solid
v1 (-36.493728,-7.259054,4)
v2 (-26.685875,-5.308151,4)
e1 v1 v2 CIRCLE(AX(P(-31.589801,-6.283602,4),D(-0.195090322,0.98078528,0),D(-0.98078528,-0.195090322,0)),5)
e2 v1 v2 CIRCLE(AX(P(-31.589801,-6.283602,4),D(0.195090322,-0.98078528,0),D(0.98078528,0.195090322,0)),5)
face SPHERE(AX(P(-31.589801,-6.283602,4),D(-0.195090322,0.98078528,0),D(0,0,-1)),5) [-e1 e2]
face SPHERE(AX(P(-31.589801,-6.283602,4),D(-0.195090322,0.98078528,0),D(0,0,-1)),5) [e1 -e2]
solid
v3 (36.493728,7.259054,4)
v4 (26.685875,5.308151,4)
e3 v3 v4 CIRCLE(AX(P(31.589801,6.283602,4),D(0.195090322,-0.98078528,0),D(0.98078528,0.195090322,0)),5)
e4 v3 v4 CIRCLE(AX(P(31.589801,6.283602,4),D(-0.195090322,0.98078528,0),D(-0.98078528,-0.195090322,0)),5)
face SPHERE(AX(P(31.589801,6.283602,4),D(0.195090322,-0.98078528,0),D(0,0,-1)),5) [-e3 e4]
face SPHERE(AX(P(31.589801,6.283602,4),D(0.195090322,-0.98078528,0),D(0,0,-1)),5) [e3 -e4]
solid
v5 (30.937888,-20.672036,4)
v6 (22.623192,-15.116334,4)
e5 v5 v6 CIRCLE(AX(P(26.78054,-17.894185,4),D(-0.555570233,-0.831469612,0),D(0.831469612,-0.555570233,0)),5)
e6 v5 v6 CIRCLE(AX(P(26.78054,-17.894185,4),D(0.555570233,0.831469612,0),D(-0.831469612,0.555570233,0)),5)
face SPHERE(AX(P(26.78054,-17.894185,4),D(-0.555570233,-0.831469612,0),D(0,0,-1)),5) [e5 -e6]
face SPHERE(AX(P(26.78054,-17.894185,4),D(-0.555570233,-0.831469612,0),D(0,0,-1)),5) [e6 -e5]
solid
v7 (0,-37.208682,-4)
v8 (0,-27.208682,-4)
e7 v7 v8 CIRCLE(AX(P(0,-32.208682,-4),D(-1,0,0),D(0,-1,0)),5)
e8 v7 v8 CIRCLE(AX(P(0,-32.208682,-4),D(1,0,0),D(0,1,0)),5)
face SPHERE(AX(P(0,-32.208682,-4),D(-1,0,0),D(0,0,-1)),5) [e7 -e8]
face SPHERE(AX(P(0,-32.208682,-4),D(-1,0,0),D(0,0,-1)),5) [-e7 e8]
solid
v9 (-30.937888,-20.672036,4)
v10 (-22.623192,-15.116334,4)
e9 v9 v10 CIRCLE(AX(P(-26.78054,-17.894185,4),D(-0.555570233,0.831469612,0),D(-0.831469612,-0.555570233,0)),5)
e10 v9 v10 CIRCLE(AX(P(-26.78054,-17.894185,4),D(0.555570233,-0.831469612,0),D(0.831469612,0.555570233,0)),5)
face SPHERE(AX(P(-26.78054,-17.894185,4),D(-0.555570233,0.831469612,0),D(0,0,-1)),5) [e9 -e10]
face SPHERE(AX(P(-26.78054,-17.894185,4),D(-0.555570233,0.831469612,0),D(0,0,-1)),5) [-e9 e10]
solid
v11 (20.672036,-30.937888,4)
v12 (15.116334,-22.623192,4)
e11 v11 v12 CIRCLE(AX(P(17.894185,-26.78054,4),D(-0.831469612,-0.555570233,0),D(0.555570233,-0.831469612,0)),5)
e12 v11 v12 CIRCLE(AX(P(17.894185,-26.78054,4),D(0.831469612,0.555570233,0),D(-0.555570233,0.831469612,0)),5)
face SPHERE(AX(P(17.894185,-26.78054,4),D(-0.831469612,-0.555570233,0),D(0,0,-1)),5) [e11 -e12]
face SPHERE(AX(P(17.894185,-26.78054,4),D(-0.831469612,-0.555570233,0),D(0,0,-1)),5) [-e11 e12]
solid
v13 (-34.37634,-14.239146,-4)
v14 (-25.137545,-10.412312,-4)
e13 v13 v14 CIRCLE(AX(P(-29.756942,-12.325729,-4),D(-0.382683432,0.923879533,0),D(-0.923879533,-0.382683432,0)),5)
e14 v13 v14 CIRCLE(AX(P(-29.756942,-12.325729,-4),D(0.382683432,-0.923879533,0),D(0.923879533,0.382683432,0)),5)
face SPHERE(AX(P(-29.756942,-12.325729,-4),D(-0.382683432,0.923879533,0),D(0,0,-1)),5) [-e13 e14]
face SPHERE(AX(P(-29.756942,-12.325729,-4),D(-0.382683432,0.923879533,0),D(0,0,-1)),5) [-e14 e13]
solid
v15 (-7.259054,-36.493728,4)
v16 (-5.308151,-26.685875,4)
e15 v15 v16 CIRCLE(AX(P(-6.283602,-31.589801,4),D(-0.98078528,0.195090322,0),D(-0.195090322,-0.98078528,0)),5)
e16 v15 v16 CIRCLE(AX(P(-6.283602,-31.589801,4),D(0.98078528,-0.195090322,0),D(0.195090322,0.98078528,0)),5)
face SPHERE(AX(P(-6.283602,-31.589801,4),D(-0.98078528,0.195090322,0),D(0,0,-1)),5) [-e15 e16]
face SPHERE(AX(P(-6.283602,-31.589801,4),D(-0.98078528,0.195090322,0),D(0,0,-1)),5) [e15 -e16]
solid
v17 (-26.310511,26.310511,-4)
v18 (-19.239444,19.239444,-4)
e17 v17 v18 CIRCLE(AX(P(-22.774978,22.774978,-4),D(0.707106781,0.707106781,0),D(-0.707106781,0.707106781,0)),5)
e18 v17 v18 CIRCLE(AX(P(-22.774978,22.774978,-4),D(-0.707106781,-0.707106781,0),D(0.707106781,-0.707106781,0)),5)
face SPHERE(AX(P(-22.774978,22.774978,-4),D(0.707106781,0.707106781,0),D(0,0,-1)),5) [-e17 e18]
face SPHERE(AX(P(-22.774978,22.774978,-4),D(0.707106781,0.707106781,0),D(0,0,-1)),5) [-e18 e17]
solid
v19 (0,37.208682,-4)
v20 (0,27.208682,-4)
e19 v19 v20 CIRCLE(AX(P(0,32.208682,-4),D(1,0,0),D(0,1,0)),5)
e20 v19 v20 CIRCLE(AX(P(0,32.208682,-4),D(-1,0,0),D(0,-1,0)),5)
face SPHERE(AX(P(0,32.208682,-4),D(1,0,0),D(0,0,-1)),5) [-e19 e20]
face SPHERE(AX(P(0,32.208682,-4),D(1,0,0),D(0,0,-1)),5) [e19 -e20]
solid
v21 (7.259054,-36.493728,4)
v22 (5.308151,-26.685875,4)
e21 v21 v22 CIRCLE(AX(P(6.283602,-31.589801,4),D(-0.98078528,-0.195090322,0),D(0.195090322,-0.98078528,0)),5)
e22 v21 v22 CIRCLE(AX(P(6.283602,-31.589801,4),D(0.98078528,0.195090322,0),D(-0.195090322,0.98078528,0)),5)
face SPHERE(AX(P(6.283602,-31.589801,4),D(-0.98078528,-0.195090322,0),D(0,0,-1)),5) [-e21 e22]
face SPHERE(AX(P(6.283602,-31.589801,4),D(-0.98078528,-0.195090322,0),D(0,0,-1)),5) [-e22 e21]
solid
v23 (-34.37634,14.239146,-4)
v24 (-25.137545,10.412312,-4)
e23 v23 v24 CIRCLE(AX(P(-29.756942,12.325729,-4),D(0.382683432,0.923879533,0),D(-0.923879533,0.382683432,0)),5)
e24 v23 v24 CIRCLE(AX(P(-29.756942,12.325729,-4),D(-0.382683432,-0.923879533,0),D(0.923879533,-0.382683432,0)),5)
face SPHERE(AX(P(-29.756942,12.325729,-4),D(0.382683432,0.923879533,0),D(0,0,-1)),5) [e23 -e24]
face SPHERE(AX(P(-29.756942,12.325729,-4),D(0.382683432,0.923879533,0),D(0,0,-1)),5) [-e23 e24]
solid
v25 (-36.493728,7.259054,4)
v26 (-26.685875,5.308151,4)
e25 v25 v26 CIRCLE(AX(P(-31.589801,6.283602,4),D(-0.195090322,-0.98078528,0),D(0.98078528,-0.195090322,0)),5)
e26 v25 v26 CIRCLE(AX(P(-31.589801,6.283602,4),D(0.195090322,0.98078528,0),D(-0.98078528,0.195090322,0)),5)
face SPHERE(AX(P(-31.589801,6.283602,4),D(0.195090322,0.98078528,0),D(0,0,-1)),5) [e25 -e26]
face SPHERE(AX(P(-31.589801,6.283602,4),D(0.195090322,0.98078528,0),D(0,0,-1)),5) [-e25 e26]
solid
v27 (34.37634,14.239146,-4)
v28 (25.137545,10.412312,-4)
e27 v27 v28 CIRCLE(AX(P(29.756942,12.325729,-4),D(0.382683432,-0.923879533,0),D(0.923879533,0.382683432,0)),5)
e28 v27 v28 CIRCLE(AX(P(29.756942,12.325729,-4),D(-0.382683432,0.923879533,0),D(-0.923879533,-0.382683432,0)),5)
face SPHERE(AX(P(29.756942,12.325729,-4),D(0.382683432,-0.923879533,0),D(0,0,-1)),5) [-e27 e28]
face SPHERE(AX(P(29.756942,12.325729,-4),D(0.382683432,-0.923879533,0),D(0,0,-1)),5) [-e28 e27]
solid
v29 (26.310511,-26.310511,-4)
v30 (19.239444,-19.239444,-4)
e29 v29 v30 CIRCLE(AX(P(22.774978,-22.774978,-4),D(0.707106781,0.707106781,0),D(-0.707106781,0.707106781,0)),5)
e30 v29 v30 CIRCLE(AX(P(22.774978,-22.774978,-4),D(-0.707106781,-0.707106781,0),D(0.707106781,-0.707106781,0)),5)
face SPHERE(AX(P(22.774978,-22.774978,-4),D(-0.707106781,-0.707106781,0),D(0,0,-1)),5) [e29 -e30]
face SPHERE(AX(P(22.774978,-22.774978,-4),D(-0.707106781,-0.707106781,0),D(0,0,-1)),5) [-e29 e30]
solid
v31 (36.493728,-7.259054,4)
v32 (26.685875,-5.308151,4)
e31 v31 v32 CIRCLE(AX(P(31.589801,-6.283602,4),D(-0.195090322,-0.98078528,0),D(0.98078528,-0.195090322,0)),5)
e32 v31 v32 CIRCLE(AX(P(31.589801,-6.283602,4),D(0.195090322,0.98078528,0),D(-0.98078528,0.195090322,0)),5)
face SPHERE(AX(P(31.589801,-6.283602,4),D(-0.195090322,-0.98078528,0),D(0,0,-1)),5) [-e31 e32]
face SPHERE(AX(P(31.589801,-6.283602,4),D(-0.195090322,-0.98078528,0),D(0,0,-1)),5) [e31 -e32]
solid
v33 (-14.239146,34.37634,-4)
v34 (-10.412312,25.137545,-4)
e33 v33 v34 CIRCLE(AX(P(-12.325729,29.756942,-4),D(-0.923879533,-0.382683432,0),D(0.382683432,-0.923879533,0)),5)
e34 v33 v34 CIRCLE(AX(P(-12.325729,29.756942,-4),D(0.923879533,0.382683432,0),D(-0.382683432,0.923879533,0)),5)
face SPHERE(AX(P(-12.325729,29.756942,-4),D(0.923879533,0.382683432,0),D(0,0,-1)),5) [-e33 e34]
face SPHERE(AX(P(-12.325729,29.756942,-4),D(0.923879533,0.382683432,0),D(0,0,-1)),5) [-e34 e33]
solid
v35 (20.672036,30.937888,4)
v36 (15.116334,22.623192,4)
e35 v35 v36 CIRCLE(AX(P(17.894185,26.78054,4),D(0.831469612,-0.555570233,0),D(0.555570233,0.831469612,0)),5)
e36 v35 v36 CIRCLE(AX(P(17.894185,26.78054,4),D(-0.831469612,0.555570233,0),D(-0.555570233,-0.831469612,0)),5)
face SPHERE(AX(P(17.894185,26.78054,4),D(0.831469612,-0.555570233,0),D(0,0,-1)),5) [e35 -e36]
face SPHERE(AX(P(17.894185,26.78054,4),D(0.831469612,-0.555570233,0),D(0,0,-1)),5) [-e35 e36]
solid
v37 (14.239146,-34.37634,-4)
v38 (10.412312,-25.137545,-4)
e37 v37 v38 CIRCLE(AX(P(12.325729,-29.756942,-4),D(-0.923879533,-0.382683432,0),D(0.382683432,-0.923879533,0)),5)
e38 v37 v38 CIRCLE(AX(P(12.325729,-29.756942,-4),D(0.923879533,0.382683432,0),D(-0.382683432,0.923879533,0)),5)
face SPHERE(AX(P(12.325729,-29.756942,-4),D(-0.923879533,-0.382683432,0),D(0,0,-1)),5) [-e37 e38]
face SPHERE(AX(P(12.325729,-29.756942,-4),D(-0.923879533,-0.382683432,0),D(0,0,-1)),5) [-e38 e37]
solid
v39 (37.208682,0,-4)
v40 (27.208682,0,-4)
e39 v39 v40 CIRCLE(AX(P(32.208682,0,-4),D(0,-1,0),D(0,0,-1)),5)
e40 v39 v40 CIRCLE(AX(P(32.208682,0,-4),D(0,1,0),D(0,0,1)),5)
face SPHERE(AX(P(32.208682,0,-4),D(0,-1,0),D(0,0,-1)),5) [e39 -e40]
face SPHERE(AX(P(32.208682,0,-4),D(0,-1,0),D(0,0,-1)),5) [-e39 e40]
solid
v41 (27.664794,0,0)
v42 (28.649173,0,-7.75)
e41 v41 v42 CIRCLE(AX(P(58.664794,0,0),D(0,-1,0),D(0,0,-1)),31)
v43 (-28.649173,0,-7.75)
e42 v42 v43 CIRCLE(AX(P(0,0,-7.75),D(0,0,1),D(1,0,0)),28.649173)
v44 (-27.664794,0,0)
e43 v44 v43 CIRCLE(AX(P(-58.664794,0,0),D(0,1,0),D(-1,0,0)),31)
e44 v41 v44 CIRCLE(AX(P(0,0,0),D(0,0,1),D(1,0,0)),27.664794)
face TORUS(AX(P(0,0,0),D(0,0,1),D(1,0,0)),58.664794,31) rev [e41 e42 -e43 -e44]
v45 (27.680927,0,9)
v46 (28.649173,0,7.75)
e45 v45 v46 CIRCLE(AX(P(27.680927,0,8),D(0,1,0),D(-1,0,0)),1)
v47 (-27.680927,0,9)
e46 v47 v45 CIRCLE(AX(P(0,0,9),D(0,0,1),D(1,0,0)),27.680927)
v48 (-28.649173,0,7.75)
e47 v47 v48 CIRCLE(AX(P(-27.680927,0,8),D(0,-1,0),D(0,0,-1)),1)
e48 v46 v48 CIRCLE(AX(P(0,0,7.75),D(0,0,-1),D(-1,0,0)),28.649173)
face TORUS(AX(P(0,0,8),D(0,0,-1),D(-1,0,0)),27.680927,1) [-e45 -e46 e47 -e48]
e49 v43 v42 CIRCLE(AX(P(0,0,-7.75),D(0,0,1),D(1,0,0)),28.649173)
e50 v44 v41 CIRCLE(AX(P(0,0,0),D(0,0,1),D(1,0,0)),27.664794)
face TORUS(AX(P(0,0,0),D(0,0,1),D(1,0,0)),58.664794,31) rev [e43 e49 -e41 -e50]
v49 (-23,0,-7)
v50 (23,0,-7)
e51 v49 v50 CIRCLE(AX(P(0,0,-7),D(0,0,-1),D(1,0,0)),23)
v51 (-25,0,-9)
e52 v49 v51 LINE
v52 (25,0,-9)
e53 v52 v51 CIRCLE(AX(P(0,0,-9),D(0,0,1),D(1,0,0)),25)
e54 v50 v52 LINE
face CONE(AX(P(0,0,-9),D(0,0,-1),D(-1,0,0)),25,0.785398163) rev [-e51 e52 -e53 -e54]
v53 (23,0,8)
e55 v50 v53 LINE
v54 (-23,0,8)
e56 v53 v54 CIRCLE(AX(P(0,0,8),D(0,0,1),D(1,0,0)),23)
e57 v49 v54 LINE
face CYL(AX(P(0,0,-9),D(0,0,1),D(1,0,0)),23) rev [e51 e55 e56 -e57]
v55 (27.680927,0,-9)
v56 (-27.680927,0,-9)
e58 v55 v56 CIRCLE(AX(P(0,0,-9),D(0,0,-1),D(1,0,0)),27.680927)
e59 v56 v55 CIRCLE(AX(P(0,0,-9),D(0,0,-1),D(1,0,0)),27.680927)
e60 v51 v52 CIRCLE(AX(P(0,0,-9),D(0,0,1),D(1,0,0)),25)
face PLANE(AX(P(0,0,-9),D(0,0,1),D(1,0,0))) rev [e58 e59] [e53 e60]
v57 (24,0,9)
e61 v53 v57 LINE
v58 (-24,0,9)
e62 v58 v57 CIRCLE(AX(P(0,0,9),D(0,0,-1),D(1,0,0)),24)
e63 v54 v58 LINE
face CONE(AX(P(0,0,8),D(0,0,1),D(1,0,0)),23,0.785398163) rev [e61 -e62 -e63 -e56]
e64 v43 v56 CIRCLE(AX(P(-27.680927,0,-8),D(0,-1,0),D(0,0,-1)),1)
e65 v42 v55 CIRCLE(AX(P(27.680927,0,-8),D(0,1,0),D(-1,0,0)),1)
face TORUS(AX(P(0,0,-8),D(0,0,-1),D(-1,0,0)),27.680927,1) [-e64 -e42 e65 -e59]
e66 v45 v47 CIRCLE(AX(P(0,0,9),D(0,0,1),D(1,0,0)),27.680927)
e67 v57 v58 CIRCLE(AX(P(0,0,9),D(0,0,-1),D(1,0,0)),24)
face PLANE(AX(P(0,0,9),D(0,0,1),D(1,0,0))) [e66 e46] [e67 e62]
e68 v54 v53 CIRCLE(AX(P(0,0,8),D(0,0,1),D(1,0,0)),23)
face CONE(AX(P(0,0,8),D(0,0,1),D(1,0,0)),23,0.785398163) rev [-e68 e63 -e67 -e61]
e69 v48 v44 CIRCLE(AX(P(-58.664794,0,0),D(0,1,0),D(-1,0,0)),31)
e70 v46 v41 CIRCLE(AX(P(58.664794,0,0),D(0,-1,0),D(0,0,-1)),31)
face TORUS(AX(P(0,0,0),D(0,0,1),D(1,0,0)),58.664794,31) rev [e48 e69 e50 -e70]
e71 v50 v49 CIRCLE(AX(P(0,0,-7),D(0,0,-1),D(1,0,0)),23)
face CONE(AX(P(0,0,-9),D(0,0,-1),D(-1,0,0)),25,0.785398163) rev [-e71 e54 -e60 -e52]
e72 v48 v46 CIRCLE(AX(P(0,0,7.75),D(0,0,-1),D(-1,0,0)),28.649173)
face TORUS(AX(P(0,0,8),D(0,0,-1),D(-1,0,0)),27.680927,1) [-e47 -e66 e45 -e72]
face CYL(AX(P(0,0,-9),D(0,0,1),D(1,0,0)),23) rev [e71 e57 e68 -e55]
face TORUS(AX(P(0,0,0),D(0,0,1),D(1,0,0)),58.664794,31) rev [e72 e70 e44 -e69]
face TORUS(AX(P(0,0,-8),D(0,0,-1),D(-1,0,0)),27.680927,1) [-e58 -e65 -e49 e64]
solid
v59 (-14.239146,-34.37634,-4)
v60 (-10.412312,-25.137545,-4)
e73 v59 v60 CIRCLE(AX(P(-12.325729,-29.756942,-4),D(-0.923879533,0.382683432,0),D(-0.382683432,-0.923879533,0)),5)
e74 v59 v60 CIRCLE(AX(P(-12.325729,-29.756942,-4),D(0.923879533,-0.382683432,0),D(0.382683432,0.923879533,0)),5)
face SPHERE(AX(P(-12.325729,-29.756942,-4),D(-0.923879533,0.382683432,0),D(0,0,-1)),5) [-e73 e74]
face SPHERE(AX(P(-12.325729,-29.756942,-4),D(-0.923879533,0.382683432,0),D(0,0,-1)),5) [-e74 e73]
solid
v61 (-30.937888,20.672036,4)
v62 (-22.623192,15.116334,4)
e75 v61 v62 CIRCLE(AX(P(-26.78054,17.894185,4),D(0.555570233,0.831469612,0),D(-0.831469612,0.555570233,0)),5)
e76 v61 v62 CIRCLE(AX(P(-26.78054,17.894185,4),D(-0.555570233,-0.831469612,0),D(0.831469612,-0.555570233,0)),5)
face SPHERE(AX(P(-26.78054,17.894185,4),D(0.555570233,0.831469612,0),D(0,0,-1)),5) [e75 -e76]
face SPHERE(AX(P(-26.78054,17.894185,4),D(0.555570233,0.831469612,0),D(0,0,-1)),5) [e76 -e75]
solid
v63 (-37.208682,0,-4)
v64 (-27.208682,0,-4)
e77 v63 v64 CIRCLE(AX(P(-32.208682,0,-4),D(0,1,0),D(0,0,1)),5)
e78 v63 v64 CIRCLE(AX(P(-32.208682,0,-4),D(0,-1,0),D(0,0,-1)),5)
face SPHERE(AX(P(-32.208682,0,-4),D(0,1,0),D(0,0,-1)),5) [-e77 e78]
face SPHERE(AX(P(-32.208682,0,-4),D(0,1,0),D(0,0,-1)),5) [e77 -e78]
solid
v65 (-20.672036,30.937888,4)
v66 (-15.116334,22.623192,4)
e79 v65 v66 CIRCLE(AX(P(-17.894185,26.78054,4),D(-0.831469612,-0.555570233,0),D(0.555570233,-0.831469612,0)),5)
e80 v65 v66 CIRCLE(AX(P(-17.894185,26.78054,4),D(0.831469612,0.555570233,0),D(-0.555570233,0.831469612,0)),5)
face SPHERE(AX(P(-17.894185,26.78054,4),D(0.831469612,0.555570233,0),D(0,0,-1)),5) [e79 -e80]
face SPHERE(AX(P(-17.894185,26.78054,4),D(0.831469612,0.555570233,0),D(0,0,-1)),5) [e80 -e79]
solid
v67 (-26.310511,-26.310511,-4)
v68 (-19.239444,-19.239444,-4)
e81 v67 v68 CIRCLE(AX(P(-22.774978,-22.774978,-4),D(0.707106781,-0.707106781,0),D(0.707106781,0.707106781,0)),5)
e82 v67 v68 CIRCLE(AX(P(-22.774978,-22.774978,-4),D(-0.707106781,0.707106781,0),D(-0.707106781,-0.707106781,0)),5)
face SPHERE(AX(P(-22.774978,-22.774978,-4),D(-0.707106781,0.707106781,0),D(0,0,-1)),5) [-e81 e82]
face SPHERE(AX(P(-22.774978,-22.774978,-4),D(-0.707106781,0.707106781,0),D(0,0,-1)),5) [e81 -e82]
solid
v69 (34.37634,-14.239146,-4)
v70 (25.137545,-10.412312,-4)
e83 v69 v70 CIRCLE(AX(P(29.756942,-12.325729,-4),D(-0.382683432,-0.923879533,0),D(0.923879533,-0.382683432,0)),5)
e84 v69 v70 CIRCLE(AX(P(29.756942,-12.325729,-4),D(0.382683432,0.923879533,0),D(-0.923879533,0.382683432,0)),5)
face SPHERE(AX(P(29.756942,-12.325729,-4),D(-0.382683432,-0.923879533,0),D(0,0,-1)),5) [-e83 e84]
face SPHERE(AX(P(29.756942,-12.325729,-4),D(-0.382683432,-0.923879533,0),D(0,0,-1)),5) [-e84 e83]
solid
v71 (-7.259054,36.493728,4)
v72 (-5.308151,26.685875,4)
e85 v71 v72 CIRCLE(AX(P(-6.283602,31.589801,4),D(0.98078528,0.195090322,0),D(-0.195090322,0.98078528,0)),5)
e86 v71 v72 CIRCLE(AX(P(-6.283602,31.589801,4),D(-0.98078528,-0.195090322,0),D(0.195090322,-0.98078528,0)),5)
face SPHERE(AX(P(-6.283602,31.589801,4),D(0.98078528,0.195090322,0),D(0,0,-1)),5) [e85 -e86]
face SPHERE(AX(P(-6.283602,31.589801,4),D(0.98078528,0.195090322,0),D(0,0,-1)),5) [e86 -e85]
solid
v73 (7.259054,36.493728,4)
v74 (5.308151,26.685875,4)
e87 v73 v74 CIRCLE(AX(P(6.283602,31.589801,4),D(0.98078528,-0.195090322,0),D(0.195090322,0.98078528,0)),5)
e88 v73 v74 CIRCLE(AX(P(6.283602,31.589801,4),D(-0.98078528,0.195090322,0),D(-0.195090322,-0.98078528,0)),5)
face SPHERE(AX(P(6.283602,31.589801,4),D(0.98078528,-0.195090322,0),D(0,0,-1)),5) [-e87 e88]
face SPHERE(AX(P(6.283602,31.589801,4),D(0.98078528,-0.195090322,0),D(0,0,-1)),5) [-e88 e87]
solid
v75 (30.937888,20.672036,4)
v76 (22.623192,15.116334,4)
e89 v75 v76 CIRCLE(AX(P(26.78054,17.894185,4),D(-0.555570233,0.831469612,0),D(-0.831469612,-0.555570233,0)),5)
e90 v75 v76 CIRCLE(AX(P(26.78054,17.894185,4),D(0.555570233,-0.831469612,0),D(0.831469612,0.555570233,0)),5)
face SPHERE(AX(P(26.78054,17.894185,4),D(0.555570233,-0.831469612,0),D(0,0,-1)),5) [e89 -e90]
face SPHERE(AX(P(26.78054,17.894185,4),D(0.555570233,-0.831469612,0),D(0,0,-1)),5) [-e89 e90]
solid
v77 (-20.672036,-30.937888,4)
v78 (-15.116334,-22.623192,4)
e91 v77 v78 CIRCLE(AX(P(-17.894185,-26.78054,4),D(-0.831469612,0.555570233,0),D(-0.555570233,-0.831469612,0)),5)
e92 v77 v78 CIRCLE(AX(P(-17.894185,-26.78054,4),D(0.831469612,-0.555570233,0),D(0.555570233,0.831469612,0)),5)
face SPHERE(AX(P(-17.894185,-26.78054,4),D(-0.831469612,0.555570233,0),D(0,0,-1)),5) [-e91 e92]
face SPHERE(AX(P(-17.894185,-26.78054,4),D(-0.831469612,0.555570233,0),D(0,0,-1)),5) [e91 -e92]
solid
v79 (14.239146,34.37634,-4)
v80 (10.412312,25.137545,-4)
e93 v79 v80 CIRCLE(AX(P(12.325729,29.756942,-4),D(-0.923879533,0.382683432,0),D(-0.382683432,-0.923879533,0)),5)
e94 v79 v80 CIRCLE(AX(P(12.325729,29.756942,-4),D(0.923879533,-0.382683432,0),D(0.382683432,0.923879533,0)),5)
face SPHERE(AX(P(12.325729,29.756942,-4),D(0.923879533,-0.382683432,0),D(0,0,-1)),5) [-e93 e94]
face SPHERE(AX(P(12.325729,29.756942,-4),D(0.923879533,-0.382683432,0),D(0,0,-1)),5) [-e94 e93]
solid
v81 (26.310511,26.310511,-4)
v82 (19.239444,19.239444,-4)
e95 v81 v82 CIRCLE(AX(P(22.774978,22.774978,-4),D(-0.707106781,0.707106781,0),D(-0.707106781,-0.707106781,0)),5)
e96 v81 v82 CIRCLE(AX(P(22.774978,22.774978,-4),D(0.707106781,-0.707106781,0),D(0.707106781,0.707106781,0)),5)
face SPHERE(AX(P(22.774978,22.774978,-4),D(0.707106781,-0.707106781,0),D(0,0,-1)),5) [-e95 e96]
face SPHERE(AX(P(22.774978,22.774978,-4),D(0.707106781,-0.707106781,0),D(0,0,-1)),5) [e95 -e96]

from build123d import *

# Parameters (mm, degrees)
SKETCH1_R           = 29
BOSS_EXTRUDE1_DEPTH = 9
CIRPATTERN4_COUNT   = 16
CIRPATTERN5_COUNT   = 16
SKETCH6_R           = 23
CUT_EXTRUDE1_DEPTH  = 56.614494957
CHAMFER1_SIZE       = 1
CHAMFER2_SIZE       = 2
FILLET1_R           = 1


with BuildPart() as part:
    # Sketch1 → Boss-Extrude1 (new, symmetric)
    with BuildSketch(Plane.XY):
        Circle(SKETCH1_R)
    extrude(amount=BOSS_EXTRUDE1_DEPTH, both=True)

    # Sketch2 → Cut-Revolve1 (revolve, cut)
    with BuildSketch(Plane(origin=(0, 0, 0), x_dir=(1, 0, 0), z_dir=(0, 1, 0))):
        with BuildLine():
            Line((29, 9), (29, -9))
            ThreePointArc((29, -9), (27.664793948, 0), (29, 9))
        make_face()
    revolve(axis=Axis((0, 0, 0), (0, 0, -1)), mode=Mode.SUBTRACT)

    # Sketch6 → Cut-Extrude1 (cut, through all)
    with BuildSketch(Plane.XY.offset(9)):
        Circle(SKETCH6_R)
    extrude(amount=-CUT_EXTRUDE1_DEPTH, mode=Mode.SUBTRACT)

    # Chamfer1
    chamfer1_edges = [part.edges().sort_by_distance(p)[0] for p in [
        (-23, 0, 9),
    ]]
    chamfer(chamfer1_edges, length=CHAMFER1_SIZE)

    # Chamfer2
    chamfer2_edges = [part.edges().sort_by_distance(p)[0] for p in [
        (-23, 0, -9),
    ]]
    chamfer(chamfer2_edges, length=CHAMFER2_SIZE)

    # Fillet1
    fillet1_edges = [part.edges().sort_by_distance(p)[0] for p in [
        (-29, 0, 9),
        (-29, 0, -9),
    ]]
    fillet(fillet1_edges, radius=FILLET1_R)


with BuildPart() as body_2:
    # Sketch3 → Revolve1 (revolve)
    with BuildSketch(Plane(origin=(0, 0, 0), x_dir=(1, 0, 0), z_dir=(0, 1, 0))):
        with BuildLine():
            Line((27.208682114, 4), (37.208682114, 4))
            ThreePointArc((37.208682114, 4), (32.208682114, 9), (27.208682114, 4))
        make_face()
    revolve(axis=Axis((27.208682114, 0, -4), (1, 0, 0)))


with BuildPart() as cirpattern4_1:
    # CirPattern4: pattern copy
    add(body_2.part.rotate(Axis((0, 0, 0), (0, 0, 1)), 1 * 360 / CIRPATTERN4_COUNT))


with BuildPart() as cirpattern4_2:
    # CirPattern4: pattern copy
    add(body_2.part.rotate(Axis((0, 0, 0), (0, 0, 1)), 2 * 360 / CIRPATTERN4_COUNT))


with BuildPart() as cirpattern4_3:
    # CirPattern4: pattern copy
    add(body_2.part.rotate(Axis((0, 0, 0), (0, 0, 1)), 3 * 360 / CIRPATTERN4_COUNT))


with BuildPart() as cirpattern4_4:
    # CirPattern4: pattern copy
    add(body_2.part.rotate(Axis((0, 0, 0), (0, 0, 1)), 4 * 360 / CIRPATTERN4_COUNT))


with BuildPart() as cirpattern4_5:
    # CirPattern4: pattern copy
    add(body_2.part.rotate(Axis((0, 0, 0), (0, 0, 1)), 5 * 360 / CIRPATTERN4_COUNT))


with BuildPart() as cirpattern4_6:
    # CirPattern4: pattern copy
    add(body_2.part.rotate(Axis((0, 0, 0), (0, 0, 1)), 6 * 360 / CIRPATTERN4_COUNT))


with BuildPart() as cirpattern4_7:
    # CirPattern4: pattern copy
    add(body_2.part.rotate(Axis((0, 0, 0), (0, 0, 1)), 7 * 360 / CIRPATTERN4_COUNT))


with BuildPart() as cirpattern4_8:
    # CirPattern4: pattern copy
    add(body_2.part.rotate(Axis((0, 0, 0), (0, 0, 1)), 8 * 360 / CIRPATTERN4_COUNT))


with BuildPart() as cirpattern4_9:
    # CirPattern4: pattern copy
    add(body_2.part.rotate(Axis((0, 0, 0), (0, 0, 1)), 9 * 360 / CIRPATTERN4_COUNT))


with BuildPart() as cirpattern4_10:
    # CirPattern4: pattern copy
    add(body_2.part.rotate(Axis((0, 0, 0), (0, 0, 1)), 10 * 360 / CIRPATTERN4_COUNT))


with BuildPart() as cirpattern4_11:
    # CirPattern4: pattern copy
    add(body_2.part.rotate(Axis((0, 0, 0), (0, 0, 1)), 11 * 360 / CIRPATTERN4_COUNT))


with BuildPart() as cirpattern4_12:
    # CirPattern4: pattern copy
    add(body_2.part.rotate(Axis((0, 0, 0), (0, 0, 1)), 12 * 360 / CIRPATTERN4_COUNT))


with BuildPart() as cirpattern4_13:
    # CirPattern4: pattern copy
    add(body_2.part.rotate(Axis((0, 0, 0), (0, 0, 1)), 13 * 360 / CIRPATTERN4_COUNT))


with BuildPart() as cirpattern4_14:
    # CirPattern4: pattern copy
    add(body_2.part.rotate(Axis((0, 0, 0), (0, 0, 1)), 14 * 360 / CIRPATTERN4_COUNT))


with BuildPart() as cirpattern4_15:
    # CirPattern4: pattern copy
    add(body_2.part.rotate(Axis((0, 0, 0), (0, 0, 1)), 15 * 360 / CIRPATTERN4_COUNT))


with BuildPart() as body_18:
    # Sketch5 → Revolve2 (revolve)
    with BuildSketch(Plane(origin=(0, 0, 0), x_dir=(0.8314696123025446, 0.5555702330196034, 0), z_dir=(-0.5555702330196033, 0.8314696123025445, 0))):
        with BuildLine():
            Line((27.208682114, -4), (37.208682114, -4))
            ThreePointArc((37.208682114, -4), (32.208682114, -9), (27.208682114, -4))
        make_face()
    revolve(axis=Axis((22.623192369, 15.116333862, 4), (0.8314696123025445, 0.5555702330196036, 0)))


with BuildPart() as cirpattern5_1:
    # CirPattern5: pattern copy
    add(body_18.part.rotate(Axis((0, 0, 0), (0, 0, 1)), 1 * 360 / CIRPATTERN5_COUNT))


with BuildPart() as cirpattern5_2:
    # CirPattern5: pattern copy
    add(body_18.part.rotate(Axis((0, 0, 0), (0, 0, 1)), 2 * 360 / CIRPATTERN5_COUNT))


with BuildPart() as cirpattern5_3:
    # CirPattern5: pattern copy
    add(body_18.part.rotate(Axis((0, 0, 0), (0, 0, 1)), 3 * 360 / CIRPATTERN5_COUNT))


with BuildPart() as cirpattern5_4:
    # CirPattern5: pattern copy
    add(body_18.part.rotate(Axis((0, 0, 0), (0, 0, 1)), 4 * 360 / CIRPATTERN5_COUNT))


with BuildPart() as cirpattern5_5:
    # CirPattern5: pattern copy
    add(body_18.part.rotate(Axis((0, 0, 0), (0, 0, 1)), 5 * 360 / CIRPATTERN5_COUNT))


with BuildPart() as cirpattern5_6:
    # CirPattern5: pattern copy
    add(body_18.part.rotate(Axis((0, 0, 0), (0, 0, 1)), 6 * 360 / CIRPATTERN5_COUNT))


with BuildPart() as cirpattern5_7:
    # CirPattern5: pattern copy
    add(body_18.part.rotate(Axis((0, 0, 0), (0, 0, 1)), 7 * 360 / CIRPATTERN5_COUNT))


with BuildPart() as cirpattern5_8:
    # CirPattern5: pattern copy
    add(body_18.part.rotate(Axis((0, 0, 0), (0, 0, 1)), 8 * 360 / CIRPATTERN5_COUNT))


with BuildPart() as cirpattern5_9:
    # CirPattern5: pattern copy
    add(body_18.part.rotate(Axis((0, 0, 0), (0, 0, 1)), 9 * 360 / CIRPATTERN5_COUNT))


with BuildPart() as cirpattern5_10:
    # CirPattern5: pattern copy
    add(body_18.part.rotate(Axis((0, 0, 0), (0, 0, 1)), 10 * 360 / CIRPATTERN5_COUNT))


with BuildPart() as cirpattern5_11:
    # CirPattern5: pattern copy
    add(body_18.part.rotate(Axis((0, 0, 0), (0, 0, 1)), 11 * 360 / CIRPATTERN5_COUNT))


with BuildPart() as cirpattern5_12:
    # CirPattern5: pattern copy
    add(body_18.part.rotate(Axis((0, 0, 0), (0, 0, 1)), 12 * 360 / CIRPATTERN5_COUNT))


with BuildPart() as cirpattern5_13:
    # CirPattern5: pattern copy
    add(body_18.part.rotate(Axis((0, 0, 0), (0, 0, 1)), 13 * 360 / CIRPATTERN5_COUNT))


with BuildPart() as cirpattern5_14:
    # CirPattern5: pattern copy
    add(body_18.part.rotate(Axis((0, 0, 0), (0, 0, 1)), 14 * 360 / CIRPATTERN5_COUNT))


with BuildPart() as cirpattern5_15:
    # CirPattern5: pattern copy
    add(body_18.part.rotate(Axis((0, 0, 0), (0, 0, 1)), 15 * 360 / CIRPATTERN5_COUNT))


solid = Compound([part.part, body_2.part, cirpattern4_1.part, cirpattern4_2.part, cirpattern4_3.part, cirpattern4_4.part, cirpattern4_5.part, cirpattern4_6.part, cirpattern4_7.part, cirpattern4_8.part, cirpattern4_9.part, cirpattern4_10.part, cirpattern4_11.part, cirpattern4_12.part, cirpattern4_13.part, cirpattern4_14.part, cirpattern4_15.part, body_18.part, cirpattern5_1.part, cirpattern5_2.part, cirpattern5_3.part, cirpattern5_4.part, cirpattern5_5.part, cirpattern5_6.part, cirpattern5_7.part, cirpattern5_8.part, cirpattern5_9.part, cirpattern5_10.part, cirpattern5_11.part, cirpattern5_12.part, cirpattern5_13.part, cirpattern5_14.part, cirpattern5_15.part])
